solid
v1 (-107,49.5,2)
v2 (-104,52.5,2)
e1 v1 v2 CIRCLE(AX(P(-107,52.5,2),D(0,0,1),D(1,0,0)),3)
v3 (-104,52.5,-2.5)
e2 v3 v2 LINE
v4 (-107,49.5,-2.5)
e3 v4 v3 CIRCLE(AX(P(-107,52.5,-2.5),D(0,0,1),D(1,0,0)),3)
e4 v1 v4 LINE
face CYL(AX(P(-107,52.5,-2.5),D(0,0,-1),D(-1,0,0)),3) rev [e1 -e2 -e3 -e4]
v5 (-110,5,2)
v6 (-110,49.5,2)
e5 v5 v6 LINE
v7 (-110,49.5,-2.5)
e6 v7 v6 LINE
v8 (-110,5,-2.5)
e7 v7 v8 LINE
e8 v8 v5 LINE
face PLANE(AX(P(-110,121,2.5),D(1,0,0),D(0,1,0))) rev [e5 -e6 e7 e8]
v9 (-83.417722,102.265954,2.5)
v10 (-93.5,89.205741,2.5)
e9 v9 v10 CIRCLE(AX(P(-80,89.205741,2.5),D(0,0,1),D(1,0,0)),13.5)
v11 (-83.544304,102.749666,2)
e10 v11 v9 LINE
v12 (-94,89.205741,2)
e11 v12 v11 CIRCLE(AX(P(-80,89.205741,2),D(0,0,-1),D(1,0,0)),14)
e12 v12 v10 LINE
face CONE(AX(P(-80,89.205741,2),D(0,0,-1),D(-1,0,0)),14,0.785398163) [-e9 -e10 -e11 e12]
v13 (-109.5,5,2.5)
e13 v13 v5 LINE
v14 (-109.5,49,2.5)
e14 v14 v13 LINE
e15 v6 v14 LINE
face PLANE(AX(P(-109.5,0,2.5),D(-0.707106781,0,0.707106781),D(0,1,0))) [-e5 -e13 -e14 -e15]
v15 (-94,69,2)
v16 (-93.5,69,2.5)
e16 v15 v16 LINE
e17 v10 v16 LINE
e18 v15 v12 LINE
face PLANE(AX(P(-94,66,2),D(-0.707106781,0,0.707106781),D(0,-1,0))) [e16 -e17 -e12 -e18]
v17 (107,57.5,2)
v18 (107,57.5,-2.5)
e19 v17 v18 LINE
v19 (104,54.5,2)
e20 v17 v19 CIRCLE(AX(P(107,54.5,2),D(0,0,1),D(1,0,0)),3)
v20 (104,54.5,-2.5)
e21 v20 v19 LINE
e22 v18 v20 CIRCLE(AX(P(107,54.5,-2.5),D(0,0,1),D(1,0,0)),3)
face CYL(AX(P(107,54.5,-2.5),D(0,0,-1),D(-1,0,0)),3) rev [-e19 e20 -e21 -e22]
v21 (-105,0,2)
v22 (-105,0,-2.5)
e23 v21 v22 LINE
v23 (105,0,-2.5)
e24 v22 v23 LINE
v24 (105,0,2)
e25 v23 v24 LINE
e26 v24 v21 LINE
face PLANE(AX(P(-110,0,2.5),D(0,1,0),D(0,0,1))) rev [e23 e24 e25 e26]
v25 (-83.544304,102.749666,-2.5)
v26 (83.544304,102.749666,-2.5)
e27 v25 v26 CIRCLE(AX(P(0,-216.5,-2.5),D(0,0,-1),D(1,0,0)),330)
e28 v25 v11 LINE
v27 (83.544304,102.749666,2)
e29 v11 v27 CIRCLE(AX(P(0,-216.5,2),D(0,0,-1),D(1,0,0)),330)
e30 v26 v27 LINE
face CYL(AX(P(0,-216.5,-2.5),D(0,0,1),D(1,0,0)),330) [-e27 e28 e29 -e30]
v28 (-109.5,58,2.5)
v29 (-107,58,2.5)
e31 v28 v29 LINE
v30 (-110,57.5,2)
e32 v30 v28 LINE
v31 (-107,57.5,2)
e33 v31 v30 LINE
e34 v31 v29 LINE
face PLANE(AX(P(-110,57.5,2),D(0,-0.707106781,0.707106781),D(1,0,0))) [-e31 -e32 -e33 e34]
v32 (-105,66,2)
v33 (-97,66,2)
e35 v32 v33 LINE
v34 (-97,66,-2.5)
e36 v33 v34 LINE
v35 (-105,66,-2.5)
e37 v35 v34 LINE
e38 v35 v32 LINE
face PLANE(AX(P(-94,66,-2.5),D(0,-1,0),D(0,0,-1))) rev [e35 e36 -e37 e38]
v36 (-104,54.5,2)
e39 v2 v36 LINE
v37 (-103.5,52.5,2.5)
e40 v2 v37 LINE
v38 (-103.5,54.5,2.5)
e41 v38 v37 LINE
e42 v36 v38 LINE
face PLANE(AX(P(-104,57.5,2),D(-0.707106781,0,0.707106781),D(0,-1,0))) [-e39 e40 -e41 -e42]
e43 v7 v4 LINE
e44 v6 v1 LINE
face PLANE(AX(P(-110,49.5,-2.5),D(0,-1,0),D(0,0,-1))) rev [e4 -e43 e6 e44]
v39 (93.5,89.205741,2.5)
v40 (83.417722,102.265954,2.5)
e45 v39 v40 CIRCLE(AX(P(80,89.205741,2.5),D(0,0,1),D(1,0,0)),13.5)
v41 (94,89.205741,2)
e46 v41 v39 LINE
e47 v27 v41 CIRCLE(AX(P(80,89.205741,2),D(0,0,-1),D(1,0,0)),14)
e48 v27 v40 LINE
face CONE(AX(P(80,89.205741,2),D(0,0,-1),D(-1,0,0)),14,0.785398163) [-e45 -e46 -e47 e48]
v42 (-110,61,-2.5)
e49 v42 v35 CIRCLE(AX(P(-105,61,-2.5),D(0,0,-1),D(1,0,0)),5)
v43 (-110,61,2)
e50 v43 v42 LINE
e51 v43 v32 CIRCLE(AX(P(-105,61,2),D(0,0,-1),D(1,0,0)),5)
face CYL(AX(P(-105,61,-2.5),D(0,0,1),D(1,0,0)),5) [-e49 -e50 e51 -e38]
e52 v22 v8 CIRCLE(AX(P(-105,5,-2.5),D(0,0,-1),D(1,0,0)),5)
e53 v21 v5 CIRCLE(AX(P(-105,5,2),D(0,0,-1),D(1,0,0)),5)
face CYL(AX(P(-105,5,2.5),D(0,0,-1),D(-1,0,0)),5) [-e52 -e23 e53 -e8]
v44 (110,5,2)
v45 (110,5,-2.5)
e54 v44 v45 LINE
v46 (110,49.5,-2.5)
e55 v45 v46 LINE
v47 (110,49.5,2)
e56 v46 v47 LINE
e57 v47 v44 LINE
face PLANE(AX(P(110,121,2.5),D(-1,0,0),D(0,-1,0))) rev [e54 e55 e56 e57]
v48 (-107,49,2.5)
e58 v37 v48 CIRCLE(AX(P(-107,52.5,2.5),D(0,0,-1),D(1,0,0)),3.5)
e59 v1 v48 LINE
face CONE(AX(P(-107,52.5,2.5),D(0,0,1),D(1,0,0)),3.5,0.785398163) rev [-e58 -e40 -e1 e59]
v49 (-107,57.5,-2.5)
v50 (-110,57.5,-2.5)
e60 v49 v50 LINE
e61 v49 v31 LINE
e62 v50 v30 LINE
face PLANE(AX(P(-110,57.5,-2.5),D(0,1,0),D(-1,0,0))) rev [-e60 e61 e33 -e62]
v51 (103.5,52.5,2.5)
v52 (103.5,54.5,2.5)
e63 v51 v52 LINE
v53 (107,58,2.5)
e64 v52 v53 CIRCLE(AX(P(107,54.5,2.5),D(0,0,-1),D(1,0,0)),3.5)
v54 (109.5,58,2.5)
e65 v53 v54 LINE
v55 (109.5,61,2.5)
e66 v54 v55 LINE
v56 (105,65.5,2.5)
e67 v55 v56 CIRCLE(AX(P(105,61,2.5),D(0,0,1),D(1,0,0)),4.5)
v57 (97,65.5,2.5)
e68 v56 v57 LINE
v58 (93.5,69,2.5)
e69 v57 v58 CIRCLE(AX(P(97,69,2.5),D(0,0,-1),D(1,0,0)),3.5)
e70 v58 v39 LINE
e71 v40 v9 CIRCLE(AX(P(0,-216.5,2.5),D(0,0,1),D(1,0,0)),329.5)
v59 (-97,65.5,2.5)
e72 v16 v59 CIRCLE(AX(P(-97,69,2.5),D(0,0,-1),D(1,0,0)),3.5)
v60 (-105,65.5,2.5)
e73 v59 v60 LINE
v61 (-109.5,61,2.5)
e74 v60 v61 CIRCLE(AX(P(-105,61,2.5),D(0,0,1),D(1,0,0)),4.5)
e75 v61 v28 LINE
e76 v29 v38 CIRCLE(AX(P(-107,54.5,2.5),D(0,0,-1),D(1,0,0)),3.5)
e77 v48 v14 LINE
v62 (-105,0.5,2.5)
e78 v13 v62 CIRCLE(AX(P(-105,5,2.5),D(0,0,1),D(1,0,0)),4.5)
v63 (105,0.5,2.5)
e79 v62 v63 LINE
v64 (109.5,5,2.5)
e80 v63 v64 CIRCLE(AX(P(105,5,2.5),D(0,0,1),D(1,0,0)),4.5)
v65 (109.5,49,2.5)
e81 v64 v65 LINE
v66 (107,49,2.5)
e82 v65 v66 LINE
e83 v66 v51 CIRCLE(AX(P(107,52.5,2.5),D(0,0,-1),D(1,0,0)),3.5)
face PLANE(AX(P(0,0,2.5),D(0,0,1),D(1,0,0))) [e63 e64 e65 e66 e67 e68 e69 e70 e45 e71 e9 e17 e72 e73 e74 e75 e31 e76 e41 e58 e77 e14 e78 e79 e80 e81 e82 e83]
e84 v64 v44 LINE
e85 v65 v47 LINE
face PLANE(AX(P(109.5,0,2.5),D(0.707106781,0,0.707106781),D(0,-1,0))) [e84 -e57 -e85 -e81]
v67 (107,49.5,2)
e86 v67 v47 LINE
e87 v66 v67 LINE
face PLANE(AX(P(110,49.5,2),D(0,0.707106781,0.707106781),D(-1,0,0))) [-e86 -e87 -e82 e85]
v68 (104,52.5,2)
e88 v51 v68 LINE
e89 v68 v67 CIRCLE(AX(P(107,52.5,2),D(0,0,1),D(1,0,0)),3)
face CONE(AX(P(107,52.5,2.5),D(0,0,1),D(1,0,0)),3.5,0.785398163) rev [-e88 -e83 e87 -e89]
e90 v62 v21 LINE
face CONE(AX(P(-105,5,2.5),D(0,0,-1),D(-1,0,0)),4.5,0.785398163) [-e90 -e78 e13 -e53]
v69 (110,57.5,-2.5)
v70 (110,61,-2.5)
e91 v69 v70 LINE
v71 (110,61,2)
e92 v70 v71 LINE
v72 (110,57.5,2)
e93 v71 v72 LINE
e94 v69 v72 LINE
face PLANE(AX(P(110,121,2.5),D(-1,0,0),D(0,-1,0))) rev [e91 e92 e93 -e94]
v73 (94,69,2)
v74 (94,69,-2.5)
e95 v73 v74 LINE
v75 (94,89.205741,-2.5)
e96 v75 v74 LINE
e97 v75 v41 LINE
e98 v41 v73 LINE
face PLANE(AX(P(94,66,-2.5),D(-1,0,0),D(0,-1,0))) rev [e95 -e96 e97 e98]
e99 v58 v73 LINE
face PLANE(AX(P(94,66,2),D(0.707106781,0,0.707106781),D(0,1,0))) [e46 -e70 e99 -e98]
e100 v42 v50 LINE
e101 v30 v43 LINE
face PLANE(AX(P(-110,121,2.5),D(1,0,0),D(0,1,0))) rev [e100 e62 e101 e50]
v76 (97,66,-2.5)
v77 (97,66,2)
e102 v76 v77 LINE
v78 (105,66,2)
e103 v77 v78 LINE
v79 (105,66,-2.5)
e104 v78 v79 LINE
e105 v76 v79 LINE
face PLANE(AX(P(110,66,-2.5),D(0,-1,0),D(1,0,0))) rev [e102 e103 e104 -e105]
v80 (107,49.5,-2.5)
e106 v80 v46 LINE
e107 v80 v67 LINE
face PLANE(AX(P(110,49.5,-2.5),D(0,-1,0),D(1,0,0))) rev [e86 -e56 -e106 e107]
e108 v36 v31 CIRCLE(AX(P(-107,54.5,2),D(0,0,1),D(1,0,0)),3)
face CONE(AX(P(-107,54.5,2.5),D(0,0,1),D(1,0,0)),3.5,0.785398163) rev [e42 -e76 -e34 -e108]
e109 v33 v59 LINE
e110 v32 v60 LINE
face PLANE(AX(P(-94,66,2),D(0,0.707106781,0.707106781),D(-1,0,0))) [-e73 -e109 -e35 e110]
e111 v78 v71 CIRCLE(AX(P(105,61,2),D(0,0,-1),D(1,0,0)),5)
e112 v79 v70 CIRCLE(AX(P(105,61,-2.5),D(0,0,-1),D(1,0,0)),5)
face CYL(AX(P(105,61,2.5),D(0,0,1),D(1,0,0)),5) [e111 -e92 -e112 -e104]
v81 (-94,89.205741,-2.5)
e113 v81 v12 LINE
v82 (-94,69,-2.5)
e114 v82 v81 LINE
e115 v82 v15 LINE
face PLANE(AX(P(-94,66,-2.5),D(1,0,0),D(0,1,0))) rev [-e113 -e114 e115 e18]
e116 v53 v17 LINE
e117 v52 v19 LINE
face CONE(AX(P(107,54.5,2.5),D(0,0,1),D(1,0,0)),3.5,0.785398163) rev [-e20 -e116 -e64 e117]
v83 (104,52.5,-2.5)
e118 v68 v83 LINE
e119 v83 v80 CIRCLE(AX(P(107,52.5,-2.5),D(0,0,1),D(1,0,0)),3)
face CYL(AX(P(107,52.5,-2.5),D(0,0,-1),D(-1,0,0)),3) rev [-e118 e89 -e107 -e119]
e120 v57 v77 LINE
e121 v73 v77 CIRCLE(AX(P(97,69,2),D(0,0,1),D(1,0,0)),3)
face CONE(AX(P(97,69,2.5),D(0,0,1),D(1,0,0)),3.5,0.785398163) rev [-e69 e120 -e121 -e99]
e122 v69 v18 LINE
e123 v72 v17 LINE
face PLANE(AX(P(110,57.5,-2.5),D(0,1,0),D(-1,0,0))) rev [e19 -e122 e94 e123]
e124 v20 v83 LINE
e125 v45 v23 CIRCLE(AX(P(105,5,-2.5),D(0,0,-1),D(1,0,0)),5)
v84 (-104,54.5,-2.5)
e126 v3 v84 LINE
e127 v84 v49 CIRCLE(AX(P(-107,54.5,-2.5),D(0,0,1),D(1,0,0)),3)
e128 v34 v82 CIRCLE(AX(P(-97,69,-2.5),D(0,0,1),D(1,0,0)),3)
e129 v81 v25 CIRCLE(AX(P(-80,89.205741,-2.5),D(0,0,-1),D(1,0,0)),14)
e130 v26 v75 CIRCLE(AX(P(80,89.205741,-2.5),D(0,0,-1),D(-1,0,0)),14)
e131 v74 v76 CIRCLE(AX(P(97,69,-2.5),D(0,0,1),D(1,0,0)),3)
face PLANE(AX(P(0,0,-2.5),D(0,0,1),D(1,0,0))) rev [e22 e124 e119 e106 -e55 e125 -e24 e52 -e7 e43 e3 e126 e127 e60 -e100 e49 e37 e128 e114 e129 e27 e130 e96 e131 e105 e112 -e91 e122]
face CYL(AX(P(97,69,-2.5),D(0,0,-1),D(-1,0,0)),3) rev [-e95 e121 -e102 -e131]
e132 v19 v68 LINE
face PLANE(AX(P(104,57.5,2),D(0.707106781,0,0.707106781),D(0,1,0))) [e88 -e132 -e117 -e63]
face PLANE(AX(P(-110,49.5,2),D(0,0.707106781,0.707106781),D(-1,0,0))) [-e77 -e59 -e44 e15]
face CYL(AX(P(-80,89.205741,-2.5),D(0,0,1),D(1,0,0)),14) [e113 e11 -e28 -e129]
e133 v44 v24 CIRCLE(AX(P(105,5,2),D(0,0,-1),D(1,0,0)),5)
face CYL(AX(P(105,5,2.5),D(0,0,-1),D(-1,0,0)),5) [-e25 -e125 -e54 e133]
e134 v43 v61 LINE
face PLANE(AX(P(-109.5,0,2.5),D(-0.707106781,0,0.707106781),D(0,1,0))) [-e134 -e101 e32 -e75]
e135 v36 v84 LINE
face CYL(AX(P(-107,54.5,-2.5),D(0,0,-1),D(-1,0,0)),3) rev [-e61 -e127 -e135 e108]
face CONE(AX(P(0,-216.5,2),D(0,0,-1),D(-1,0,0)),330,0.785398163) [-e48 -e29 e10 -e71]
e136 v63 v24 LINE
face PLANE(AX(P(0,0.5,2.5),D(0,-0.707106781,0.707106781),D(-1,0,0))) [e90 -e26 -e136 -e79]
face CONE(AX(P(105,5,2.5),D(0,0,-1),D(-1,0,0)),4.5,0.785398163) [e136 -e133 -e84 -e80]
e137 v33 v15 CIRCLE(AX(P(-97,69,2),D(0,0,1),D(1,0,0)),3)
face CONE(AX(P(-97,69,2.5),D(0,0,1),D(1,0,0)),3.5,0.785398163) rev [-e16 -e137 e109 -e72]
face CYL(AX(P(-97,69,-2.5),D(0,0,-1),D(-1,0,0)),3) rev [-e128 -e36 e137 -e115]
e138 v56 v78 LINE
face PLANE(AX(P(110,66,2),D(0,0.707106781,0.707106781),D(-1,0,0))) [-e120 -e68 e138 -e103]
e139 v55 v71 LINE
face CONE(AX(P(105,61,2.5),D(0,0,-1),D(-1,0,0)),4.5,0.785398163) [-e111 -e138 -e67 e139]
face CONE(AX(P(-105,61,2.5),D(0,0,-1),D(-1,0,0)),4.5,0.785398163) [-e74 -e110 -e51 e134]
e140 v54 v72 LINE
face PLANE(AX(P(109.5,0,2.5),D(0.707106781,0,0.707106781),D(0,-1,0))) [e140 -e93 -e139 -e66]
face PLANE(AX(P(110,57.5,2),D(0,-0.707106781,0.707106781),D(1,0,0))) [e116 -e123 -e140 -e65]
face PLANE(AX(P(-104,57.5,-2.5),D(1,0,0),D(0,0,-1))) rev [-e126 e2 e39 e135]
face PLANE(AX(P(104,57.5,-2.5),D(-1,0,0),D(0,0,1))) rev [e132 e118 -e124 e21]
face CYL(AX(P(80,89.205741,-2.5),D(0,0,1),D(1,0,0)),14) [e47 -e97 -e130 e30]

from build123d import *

# Parameters (mm, degrees)
SKETCH_1_W          = 220
SKETCH_1_H          = 121
EXTRUDE_1_DEPTH     = 2.5
CUT_EXTRUDE_1_DEPTH = 164.603178453
SKETCH_5_W          = 6
SKETCH_5_H          = 8
CUT_EXTRUDE_2_DEPTH = 159.13680786
FILLET_1_R          = 5
FILLET_2_R          = 3
CHAMFER_1_SIZE      = 0.5


with BuildPart() as part:
    # 草图1 → 凸台-拉伸1 (new, symmetric)
    with BuildSketch(Plane.XY):
        with Locations((0, 60.5)):
            Rectangle(SKETCH_1_W, SKETCH_1_H)
    extrude(amount=EXTRUDE_1_DEPTH, both=True)

    # 草图4 → 切除-拉伸1 (cut, through all)
    with BuildSketch(Plane.XY.offset(2.5)):
        with BuildLine():
            Line((-94, 66), (-110, 66))
            Line((-110, 66), (-110, 125.2))
            Line((-110, 125.2), (110, 125.2))
            Line((110, 125.2), (110, 66))
            Line((110, 66), (94, 66))
            Line((94, 66), (94, 89.205740869))
            ThreePointArc((94, 89.205740869), (91.081973046, 97.760848899), (83.544303797, 102.749666097))
            ThreePointArc((83.544303797, 102.749666097), (0, 113.5), (-83.544303797, 102.749666097))
            ThreePointArc((-83.544303797, 102.749666097), (-91.081973046, 97.760848899), (-94, 89.205740869))
            Line((-94, 89.205740869), (-94, 66))
        make_face()
    extrude(amount=-CUT_EXTRUDE_1_DEPTH, mode=Mode.SUBTRACT)

    # 草图5 → 切除-拉伸2 (cut, through all)
    with BuildSketch(Plane.XY.offset(2.5)):
        with Locations((-107, 53.5)):
            Rectangle(SKETCH_5_W, SKETCH_5_H)
        with Locations((107, 53.5)):
            Rectangle(SKETCH_5_W, SKETCH_5_H)
    extrude(amount=-CUT_EXTRUDE_2_DEPTH, mode=Mode.SUBTRACT)

    # 圆角1
    fillet_1_edges = [part.edges().sort_by_distance(p)[0] for p in [
        (-110, 66, 0),
        (110, 66, 0),
        (110, 0, 0),
        (-110, 0, 0),
    ]]
    fillet(fillet_1_edges, radius=FILLET_1_R)

    # 圆角2
    fillet_2_edges = [part.edges().sort_by_distance(p)[0] for p in [
        (-94, 66, 0),
        (94, 66, 0),
        (-104, 57.5, 0),
        (-104, 49.5, 0),
        (104, 49.5, 0),
        (104, 57.5, 0),
    ]]
    fillet(fillet_2_edges, radius=FILLET_2_R)

    # 倒角1
    chamfer_1_edges = [part.edges().sort_by_distance(p)[0] for p in [
        (-94, 79.102870434, 2.5),
        (101, 66, 2.5),
        (-104, 53.5, 2.5),
        (-108.5, 57.5, 2.5),
        (108.5, 49.5, 2.5),
        (104, 53.5, 2.5),
        (-94.878679656, 66.878679656, 2.5),
        (94.878679656, 66.878679656, 2.5),
        (-104.878679656, 50.378679656, 2.5),
        (-104.878679656, 56.621320344, 2.5),
        (104.878679656, 50.378679656, 2.5),
        (104.878679656, 56.621320344, 2.5),
        (-91.081973046, 97.760848899, 2.5),
        (0, 113.5, 2.5),
        (91.081973046, 97.760848899, 2.5),
        (94, 79.102870434, 2.5),
        (-110, 27.25, 2.5),
        (-108.5, 49.5, 2.5),
        (110, 59.25, 2.5),
        (108.5, 57.5, 2.5),
        (-101, 66, 2.5),
        (-110, 59.25, 2.5),
        (0, 0, 2.5),
        (110, 27.25, 2.5),
        (108.535533906, 1.464466094, 2.5),
        (-108.535533906, 1.464466094, 2.5),
        (108.535533906, 64.535533906, 2.5),
        (-108.535533906, 64.535533906, 2.5),
    ]]
    chamfer(chamfer_1_edges, length=CHAMFER_1_SIZE)


solid = part.part
